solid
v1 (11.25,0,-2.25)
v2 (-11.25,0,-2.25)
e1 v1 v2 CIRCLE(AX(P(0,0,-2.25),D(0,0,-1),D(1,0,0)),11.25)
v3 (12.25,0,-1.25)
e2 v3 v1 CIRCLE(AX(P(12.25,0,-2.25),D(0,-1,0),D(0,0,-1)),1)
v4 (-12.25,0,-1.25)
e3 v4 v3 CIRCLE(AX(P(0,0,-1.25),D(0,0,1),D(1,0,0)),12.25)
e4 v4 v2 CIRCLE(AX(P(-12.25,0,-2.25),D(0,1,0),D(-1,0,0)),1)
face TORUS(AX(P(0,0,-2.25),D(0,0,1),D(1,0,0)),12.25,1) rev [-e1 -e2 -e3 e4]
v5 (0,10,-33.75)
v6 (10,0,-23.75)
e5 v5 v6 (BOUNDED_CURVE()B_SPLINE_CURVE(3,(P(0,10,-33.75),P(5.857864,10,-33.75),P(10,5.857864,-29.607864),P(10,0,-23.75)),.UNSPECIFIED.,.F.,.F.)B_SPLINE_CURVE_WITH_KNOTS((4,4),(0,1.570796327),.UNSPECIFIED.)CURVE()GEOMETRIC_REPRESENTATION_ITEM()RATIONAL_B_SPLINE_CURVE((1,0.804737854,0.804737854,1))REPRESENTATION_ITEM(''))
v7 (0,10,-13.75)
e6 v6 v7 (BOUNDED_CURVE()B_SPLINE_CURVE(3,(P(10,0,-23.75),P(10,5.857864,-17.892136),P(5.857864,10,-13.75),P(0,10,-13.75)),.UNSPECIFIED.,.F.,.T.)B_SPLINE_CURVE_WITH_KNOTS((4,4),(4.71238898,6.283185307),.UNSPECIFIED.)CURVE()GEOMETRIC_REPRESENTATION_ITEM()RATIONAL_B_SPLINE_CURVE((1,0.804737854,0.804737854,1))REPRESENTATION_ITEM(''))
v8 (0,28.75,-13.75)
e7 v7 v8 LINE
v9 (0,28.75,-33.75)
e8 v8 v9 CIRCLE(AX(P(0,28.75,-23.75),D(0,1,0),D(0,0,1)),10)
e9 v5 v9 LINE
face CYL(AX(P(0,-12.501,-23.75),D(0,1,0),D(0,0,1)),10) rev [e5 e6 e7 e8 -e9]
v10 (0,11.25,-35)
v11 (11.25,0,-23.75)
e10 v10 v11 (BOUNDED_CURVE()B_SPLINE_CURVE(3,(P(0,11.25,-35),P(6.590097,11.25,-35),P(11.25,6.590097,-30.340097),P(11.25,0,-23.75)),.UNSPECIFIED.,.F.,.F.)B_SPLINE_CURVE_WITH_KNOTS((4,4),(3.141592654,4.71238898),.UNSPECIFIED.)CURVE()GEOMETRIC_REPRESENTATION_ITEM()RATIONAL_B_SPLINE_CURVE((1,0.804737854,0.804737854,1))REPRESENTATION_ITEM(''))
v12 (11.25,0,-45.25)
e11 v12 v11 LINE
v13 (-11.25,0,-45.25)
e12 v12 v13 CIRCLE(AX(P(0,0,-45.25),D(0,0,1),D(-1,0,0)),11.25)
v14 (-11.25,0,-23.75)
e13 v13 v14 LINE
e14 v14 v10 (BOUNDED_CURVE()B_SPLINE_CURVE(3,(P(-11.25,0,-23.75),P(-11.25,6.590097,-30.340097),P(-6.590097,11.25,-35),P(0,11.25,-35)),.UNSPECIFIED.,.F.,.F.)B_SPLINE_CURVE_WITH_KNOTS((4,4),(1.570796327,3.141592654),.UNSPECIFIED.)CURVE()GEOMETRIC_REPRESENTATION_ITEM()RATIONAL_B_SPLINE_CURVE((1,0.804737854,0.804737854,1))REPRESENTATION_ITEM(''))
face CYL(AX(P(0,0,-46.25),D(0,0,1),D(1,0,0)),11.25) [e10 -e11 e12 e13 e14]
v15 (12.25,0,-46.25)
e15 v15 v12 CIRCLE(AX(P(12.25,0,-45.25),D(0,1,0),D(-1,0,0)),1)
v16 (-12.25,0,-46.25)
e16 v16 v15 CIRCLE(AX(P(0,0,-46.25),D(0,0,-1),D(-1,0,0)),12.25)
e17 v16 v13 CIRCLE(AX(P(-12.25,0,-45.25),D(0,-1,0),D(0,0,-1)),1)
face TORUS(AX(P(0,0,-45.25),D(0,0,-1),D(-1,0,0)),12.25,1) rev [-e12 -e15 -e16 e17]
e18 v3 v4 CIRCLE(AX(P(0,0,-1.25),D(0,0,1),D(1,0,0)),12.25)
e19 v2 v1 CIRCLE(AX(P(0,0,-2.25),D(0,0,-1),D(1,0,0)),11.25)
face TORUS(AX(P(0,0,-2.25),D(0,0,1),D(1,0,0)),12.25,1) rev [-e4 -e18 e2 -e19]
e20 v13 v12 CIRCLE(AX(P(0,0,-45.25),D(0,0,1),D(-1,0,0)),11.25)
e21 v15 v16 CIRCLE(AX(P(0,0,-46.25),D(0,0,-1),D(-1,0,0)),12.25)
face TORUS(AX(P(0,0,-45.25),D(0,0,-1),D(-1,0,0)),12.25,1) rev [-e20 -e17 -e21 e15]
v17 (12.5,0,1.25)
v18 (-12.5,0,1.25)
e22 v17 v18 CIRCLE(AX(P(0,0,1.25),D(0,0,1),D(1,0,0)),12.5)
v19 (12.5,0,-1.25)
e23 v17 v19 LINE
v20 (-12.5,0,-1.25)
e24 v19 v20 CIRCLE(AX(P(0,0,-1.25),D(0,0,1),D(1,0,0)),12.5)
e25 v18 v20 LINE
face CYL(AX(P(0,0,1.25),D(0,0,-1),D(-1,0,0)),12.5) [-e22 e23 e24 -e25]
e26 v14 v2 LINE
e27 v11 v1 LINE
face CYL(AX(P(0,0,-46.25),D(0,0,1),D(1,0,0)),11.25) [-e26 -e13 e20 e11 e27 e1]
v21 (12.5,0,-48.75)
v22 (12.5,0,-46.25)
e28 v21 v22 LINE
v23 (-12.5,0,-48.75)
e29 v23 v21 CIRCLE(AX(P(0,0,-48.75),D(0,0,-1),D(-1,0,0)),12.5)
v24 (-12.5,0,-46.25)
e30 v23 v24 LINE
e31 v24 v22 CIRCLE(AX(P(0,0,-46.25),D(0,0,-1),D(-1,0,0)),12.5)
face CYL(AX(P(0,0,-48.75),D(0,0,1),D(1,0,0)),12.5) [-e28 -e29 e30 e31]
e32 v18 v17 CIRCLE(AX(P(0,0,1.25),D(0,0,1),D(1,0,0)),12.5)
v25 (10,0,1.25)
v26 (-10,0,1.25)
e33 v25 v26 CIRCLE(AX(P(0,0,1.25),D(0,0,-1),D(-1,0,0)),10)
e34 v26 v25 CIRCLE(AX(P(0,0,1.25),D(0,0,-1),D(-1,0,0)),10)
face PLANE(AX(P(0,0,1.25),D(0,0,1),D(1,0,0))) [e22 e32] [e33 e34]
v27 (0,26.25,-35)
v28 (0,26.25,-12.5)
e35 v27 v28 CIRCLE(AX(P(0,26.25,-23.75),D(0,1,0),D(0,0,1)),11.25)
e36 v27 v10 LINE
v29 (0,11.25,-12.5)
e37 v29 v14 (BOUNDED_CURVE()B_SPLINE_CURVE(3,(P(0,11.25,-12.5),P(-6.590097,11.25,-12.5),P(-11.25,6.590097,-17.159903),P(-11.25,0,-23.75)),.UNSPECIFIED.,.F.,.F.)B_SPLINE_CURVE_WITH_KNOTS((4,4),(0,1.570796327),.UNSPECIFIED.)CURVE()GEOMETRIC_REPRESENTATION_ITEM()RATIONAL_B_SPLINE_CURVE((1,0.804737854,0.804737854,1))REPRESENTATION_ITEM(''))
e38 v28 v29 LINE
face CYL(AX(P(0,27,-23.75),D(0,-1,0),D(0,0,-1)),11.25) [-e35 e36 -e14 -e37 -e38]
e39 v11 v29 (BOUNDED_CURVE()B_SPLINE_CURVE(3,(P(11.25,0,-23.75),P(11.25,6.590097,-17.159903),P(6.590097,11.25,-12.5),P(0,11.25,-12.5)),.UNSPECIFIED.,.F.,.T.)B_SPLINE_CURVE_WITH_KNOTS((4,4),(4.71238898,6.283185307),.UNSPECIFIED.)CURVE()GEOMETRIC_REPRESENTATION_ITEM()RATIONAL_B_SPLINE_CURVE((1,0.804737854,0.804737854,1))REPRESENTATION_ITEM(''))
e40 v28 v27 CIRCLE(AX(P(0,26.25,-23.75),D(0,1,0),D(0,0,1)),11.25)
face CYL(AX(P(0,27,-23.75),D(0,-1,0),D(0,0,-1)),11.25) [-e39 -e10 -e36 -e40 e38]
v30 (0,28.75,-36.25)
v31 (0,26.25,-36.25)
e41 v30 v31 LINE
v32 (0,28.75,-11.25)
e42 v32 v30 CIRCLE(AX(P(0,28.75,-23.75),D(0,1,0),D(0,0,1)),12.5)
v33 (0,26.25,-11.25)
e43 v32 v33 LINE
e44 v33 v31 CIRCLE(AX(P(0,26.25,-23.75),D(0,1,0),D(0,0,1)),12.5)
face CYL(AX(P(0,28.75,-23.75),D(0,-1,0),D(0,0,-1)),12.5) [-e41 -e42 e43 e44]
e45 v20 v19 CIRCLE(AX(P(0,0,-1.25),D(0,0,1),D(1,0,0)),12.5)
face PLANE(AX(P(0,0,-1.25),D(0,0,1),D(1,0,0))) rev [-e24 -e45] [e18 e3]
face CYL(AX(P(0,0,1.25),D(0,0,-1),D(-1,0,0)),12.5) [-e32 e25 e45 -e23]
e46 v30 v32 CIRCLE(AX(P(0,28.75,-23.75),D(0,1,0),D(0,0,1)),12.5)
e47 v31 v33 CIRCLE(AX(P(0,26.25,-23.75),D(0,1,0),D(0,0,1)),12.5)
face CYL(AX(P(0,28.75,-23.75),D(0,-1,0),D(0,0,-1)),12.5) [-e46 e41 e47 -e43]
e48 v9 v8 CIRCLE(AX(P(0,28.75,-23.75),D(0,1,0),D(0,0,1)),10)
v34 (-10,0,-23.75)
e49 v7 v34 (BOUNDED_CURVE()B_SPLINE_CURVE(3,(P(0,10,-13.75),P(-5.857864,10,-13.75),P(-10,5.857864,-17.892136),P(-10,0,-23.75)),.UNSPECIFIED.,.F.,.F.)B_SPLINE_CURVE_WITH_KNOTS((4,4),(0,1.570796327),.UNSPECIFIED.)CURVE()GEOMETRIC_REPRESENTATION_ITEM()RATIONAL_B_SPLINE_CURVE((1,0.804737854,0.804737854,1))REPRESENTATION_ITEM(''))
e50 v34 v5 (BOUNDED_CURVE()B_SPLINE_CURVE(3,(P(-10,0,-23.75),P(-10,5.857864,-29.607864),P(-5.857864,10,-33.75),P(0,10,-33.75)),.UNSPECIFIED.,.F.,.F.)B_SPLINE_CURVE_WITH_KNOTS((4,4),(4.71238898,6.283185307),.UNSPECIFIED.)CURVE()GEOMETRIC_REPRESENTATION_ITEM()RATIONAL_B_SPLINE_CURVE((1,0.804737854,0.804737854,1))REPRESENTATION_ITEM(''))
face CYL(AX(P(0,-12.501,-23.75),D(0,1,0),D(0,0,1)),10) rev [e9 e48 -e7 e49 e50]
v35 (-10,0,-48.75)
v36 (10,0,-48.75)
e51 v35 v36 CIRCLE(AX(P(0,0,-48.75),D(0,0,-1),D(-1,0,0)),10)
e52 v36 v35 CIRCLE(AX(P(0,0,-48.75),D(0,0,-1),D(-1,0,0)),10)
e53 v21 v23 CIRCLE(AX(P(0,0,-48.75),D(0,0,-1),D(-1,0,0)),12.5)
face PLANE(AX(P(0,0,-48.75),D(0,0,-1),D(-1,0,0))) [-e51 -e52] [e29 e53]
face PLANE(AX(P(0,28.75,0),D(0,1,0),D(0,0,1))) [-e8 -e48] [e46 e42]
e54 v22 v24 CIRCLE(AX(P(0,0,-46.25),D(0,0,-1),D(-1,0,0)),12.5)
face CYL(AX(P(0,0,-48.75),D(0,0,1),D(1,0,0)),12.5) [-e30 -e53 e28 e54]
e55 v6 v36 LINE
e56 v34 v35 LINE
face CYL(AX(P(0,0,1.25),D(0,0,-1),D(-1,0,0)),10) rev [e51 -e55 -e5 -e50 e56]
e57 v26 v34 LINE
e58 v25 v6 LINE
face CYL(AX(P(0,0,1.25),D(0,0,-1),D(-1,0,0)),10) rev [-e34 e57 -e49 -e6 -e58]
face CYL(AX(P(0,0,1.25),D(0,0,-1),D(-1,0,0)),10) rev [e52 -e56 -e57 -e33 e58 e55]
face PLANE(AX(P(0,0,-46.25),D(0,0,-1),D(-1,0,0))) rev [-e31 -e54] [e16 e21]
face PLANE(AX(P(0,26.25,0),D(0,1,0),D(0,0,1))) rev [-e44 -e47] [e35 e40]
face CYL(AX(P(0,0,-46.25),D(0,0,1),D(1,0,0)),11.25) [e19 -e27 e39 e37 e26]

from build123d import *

# Parameters (mm, degrees)
END_RIM_A_PROFILE_25_R       = 12.5
END_RIM_A_25_DEPTH           = 1.25
RUN_START                    = -2.5
RUN_TUBE_PROFILE_22_5_R      = 11.25
RUN_TUBE_22_5_DEPTH          = 45
END_RIM_B_PROFILE_25_R       = 12.5
END_RIM_B_25_DEPTH           = 2.5
RUN_BORE_PROFILE_20_R        = 10
RUN_BORE_20_DEPTH            = 54.033008589
RIM_FILLETS_R1_R             = 1
BRANCH_START                 = 26.25
BRANCH_RIM_25_DEPTH          = 2.5
BRANCH_TUBE_PROFILE_22_5_R   = 11.25
BRANCH_TUBE_22_5_DEPTH       = 27
RUN_BORE_CLEARANCE_PROFILE_R = 10
RUN_BORE_CLEARANCE_CUT_DEPTH = 60.015358255
BRANCH_BORE_20_REACH         = 67.072
BRANCH_BORE_20_END_RADIUS    = 10
BRANCH_BORE_PROFILE_20_R     = 10


with BuildPart() as part:
    # End Rim A Profile Ø25 → End Rim A Ø25 (new, symmetric)
    with BuildSketch(Plane.XY):
        Circle(END_RIM_A_PROFILE_25_R)
    extrude(amount=END_RIM_A_25_DEPTH, both=True)

    # Run Tube Profile Ø22.5 → Run Tube Ø22.5 (add)
    with BuildSketch(Plane.XY.offset(1.25).offset(RUN_START)):
        Circle(RUN_TUBE_PROFILE_22_5_R)
    extrude(amount=-RUN_TUBE_22_5_DEPTH)

    # End Rim B Profile Ø25 → End Rim B Ø25 (add)
    with BuildSketch(Plane(origin=(0, 0, -46.25), x_dir=(-1, 0, 0), z_dir=(0, 0, -1))):
        with Locations(Location((0, 0, 0), (0, 0, 180))):
            Circle(END_RIM_B_PROFILE_25_R)
    extrude(amount=END_RIM_B_25_DEPTH)

    # Run Bore Profile Ø20 → Run Bore Ø20 (cut, through all)
    with BuildSketch(Plane(origin=(0, 0, -48.75), x_dir=(-1, 0, 0), z_dir=(0, 0, -1))):
        Circle(RUN_BORE_PROFILE_20_R)
    extrude(amount=-RUN_BORE_20_DEPTH, mode=Mode.SUBTRACT)

    # Rim Fillets R1
    rim_fillets_r1_edges = [part.edges().sort_by_distance(p)[0] for p in [
        (-11.25, 0, -46.25),
        (-11.25, 0, -1.25),
    ]]
    fillet(rim_fillets_r1_edges, radius=RIM_FILLETS_R1_R)



with BuildPart() as body_2:
    # Branch Rim Profile Ø25 → Branch Rim Ø25 (new body)
    with BuildSketch(Plane(origin=(0, 0, 0), x_dir=(1, 0, 0), z_dir=(0, 1, 0)).offset(BRANCH_START)):
        with BuildLine():
            ThreePointArc((12.5, 23.75), (8.838834765, 32.588834765), (0, 36.25))
            Line((0, 36.25), (0, 11.25))
            ThreePointArc((0, 11.25), (8.838834765, 14.911165235), (12.5, 23.75))
        make_face()
        with BuildLine():
            Line((0, 11.25), (0, 36.25))
            ThreePointArc((0, 36.25), (-12.5, 23.75), (0, 11.25))
        make_face()
    extrude(amount=BRANCH_RIM_25_DEPTH)


with BuildPart() as part_1:
    add(part.part)

    add(body_2.part)  # Branch Tube Ø22.5 merges body 2
    # Branch Tube Profile Ø22.5 → Branch Tube Ø22.5 (add)
    with BuildSketch(Plane(origin=(0, 0, 0), x_dir=(1, 0, 0), z_dir=(0, 1, 0))):
        with Locations((0, 23.75)):
            Circle(BRANCH_TUBE_PROFILE_22_5_R)
    extrude(amount=BRANCH_TUBE_22_5_DEPTH)

    # Run Bore Clearance Profile → Run Bore Clearance Cut (cut, through all)
    with BuildSketch(Plane.XY.offset(1.25)):
        with Locations(Location((0, 0, 0), (0, 0, 180))):
            Circle(RUN_BORE_CLEARANCE_PROFILE_R)
    extrude(amount=-RUN_BORE_CLEARANCE_CUT_DEPTH, mode=Mode.SUBTRACT)

    # Branch Bore Ø20: up to this cylinder (the profile starts outside it)
    branch_bore_20_end = Plane(origin=(0, 0, -23.75), z_dir=(0, 0, -1)) * Cylinder(BRANCH_BORE_20_END_RADIUS, 155.144, mode=Mode.PRIVATE)
    # Branch Bore Profile Ø20 → Branch Bore Ø20 (cut, up to the surface)
    with BuildSketch(Plane(origin=(0, 28.75, 0), x_dir=(1, 0, 0), z_dir=(0, 1, 0)), mode=Mode.PRIVATE) as branch_bore_20_sk1:
        with Locations(Location((0, 23.75, 0), (0, 0, 270))):
            Circle(BRANCH_BORE_PROFILE_20_R)
    branch_bore_20_tool1 = extrude(branch_bore_20_sk1.sketch, amount=-BRANCH_BORE_20_REACH, mode=Mode.PRIVATE) - branch_bore_20_end
    add(branch_bore_20_tool1.solids().sort_by_distance((0, 28.75, -23.75))[0], mode=Mode.SUBTRACT)


solid = part_1.part
